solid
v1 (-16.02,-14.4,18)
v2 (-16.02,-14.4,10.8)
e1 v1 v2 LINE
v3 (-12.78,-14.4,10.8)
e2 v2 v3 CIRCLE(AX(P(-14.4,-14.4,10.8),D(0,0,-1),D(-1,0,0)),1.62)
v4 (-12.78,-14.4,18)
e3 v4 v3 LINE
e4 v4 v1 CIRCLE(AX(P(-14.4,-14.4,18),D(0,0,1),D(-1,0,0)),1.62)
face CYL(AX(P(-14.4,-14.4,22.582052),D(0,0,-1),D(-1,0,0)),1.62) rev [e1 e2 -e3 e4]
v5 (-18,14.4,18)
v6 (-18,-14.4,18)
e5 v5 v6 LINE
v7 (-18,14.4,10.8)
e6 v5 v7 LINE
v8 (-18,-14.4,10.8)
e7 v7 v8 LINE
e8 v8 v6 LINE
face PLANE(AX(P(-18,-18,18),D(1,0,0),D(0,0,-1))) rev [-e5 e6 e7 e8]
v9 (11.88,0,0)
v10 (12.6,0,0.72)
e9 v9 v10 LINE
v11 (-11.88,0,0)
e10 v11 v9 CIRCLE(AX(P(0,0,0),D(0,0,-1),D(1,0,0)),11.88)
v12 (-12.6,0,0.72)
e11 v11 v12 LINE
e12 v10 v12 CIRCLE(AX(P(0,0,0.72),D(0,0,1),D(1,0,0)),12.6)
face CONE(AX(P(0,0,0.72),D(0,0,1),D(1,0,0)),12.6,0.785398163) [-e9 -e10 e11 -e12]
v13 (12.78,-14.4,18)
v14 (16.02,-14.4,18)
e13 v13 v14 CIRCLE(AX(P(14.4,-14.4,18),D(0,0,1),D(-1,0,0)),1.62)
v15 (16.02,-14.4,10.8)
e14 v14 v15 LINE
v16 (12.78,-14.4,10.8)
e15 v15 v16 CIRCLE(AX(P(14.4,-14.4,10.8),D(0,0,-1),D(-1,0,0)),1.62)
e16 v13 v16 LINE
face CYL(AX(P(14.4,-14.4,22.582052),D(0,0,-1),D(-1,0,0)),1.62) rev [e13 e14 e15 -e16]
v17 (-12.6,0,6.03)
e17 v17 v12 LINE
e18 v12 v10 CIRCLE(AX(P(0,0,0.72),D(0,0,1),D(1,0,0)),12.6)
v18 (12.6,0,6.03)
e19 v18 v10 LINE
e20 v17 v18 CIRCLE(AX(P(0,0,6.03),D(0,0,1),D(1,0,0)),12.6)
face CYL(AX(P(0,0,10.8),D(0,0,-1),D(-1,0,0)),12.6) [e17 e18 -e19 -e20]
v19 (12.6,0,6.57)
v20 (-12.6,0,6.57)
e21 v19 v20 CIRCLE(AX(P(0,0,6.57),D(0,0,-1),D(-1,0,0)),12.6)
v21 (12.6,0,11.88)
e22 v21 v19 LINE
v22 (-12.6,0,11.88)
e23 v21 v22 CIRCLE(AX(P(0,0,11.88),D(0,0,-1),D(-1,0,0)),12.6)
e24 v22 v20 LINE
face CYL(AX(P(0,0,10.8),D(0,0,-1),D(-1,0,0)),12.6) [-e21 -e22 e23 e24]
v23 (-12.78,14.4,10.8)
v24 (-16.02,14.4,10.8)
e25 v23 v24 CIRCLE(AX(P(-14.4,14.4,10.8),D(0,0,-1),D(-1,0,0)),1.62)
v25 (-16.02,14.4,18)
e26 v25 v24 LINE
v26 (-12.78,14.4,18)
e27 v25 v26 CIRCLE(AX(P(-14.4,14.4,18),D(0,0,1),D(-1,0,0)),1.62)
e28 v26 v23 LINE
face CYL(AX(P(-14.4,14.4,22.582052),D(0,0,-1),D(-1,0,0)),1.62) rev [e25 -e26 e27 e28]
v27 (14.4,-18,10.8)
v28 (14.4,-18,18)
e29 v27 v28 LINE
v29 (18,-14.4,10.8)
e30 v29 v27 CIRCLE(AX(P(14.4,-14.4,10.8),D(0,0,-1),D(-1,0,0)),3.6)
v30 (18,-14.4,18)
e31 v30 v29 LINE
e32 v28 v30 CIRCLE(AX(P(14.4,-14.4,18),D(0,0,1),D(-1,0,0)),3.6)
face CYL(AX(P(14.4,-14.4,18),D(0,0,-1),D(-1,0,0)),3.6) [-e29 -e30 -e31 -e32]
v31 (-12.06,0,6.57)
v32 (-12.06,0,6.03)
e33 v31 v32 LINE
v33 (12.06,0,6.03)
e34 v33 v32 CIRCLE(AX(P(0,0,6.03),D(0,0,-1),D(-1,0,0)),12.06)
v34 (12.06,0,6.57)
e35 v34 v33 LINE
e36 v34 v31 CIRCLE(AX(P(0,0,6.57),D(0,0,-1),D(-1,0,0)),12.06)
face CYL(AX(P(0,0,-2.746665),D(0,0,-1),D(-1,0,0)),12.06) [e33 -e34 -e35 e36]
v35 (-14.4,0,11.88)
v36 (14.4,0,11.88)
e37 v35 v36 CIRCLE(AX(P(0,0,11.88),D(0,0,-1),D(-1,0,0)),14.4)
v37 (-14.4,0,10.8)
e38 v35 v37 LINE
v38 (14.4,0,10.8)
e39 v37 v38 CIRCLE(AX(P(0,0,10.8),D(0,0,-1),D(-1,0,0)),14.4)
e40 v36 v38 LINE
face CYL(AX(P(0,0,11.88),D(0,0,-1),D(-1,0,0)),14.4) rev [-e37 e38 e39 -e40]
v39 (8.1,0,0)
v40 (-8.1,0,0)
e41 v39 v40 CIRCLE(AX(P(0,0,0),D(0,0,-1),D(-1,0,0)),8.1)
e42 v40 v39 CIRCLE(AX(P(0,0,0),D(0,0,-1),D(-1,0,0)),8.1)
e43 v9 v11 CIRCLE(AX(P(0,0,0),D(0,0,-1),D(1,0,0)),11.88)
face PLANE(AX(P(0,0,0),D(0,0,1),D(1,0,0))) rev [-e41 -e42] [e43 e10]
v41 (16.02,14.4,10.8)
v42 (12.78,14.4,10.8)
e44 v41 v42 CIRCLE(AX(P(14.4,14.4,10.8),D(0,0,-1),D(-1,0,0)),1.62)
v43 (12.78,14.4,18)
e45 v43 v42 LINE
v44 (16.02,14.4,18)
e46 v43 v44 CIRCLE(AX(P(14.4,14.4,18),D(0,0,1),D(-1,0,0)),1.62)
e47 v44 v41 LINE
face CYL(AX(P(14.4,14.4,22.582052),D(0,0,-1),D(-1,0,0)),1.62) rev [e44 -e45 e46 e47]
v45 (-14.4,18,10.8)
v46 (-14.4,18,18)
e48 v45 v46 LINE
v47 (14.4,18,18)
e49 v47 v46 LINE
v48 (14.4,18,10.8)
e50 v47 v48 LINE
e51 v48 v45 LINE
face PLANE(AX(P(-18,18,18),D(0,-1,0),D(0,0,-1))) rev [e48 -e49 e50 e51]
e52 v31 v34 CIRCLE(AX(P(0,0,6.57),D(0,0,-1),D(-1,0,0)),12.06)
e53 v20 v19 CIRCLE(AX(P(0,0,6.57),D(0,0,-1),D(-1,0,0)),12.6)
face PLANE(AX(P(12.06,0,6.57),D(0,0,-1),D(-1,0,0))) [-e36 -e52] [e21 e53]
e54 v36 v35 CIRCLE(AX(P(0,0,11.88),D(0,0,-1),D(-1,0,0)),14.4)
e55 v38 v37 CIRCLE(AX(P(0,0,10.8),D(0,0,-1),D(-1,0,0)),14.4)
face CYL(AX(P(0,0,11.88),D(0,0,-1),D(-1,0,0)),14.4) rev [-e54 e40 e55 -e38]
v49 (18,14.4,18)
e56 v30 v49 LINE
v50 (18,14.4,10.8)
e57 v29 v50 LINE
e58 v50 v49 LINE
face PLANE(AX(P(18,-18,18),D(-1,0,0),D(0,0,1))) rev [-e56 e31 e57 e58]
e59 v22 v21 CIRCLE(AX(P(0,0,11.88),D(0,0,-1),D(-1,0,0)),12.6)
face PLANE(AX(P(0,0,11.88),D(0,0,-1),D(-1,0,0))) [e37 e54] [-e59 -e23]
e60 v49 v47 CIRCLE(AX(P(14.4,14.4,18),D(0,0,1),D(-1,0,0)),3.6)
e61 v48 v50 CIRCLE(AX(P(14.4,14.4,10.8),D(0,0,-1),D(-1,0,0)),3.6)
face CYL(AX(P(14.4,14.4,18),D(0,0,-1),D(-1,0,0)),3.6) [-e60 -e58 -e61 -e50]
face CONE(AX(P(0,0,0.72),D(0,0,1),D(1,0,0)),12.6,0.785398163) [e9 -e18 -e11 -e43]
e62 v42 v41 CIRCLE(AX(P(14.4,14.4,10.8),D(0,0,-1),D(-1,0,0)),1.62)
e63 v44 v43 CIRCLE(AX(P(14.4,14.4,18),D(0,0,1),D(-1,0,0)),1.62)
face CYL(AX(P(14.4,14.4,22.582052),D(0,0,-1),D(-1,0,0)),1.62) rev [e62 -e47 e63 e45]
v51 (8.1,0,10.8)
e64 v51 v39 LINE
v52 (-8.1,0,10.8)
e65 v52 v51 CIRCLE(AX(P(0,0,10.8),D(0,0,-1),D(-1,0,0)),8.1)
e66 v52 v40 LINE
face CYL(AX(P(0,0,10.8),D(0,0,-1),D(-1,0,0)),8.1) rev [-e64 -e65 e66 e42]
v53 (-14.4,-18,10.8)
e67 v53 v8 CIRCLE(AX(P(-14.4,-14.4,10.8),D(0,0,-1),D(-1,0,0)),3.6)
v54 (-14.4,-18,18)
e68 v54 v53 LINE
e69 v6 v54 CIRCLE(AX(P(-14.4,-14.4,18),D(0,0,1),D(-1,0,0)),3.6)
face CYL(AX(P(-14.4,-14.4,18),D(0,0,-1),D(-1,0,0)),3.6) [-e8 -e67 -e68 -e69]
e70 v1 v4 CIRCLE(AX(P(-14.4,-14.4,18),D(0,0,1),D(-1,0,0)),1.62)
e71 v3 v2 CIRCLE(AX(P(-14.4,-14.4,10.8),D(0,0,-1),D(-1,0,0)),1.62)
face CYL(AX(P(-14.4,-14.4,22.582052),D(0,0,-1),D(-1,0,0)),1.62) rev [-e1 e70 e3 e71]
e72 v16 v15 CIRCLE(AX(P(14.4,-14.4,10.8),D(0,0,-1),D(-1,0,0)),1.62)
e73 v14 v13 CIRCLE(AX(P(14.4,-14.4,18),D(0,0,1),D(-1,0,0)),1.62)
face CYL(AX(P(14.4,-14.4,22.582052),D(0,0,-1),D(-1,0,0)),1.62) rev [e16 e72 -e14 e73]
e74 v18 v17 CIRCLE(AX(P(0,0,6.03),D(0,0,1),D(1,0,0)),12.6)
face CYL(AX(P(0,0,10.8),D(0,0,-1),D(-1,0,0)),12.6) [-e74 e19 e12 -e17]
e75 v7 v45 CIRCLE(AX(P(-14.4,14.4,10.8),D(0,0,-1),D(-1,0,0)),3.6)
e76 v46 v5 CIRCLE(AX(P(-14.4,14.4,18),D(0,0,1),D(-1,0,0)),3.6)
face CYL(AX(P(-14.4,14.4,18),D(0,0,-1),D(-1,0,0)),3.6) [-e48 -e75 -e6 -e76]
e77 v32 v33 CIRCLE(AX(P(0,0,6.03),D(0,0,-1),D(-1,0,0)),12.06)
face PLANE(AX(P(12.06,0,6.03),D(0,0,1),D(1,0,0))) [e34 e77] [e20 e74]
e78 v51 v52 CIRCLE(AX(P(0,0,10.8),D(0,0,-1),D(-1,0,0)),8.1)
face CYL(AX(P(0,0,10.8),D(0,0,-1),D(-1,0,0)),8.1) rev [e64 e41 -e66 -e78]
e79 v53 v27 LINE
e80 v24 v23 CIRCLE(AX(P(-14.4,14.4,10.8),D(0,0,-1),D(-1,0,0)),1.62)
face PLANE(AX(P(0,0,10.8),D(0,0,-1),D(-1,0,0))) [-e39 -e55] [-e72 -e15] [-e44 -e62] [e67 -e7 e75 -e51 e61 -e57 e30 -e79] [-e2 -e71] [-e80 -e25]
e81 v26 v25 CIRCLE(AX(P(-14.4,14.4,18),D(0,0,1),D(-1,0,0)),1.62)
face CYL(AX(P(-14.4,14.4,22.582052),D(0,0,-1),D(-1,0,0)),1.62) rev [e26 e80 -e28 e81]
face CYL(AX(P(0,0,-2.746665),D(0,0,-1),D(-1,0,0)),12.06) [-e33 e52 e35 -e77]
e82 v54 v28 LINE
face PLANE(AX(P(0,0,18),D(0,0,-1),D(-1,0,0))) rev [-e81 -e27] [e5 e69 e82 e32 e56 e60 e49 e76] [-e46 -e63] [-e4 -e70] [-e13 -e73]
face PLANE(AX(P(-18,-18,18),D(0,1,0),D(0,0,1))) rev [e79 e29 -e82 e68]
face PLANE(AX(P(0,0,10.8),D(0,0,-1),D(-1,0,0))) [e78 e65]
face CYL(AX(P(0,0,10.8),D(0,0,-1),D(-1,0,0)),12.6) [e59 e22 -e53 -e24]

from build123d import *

# Parameters (mm, degrees)
SKETCH1_R           = 12.6
BOSS_EXTRUDE1_DEPTH = 10.8
SKETCH2_W           = 36
SKETCH2_H           = 36
BOSS_EXTRUDE2_DEPTH = 7.2
FILLET1_R           = 3.6
CHAMFER1_SIZE       = 0.72
SKETCH3_R           = 14.4
SKETCH3_R_2         = 12.6
CUT_EXTRUDE1_DEPTH  = 1.08
SKETCH4_W           = 1.08
SKETCH4_H           = 0.54
SKETCH5_R           = 1.62
CUT_EXTRUDE2_DEPTH  = 7.2
SKETCH6_R           = 8.1
CUT_EXTRUDE3_DEPTH  = 10.8


with BuildPart() as part:
    # Sketch1 → Boss-Extrude1 (new body)
    with BuildSketch(Plane.XY):
        with Locations(Location((0, 0, 0), (0, 0, 180))):
            Circle(SKETCH1_R)
    extrude(amount=BOSS_EXTRUDE1_DEPTH)

    # Sketch2 → Boss-Extrude2 (add)
    with BuildSketch(Plane.XY.offset(10.8)):
        Rectangle(SKETCH2_W, SKETCH2_H)
    extrude(amount=BOSS_EXTRUDE2_DEPTH)

    # Fillet1
    fillet1_edges = [part.edges().sort_by_distance(p)[0] for p in [
        (18, -18, 14.4),
        (18, 18, 14.4),
        (-18, 18, 14.4),
        (-18, -18, 14.4),
    ]]
    fillet(fillet1_edges, radius=FILLET1_R)

    # Chamfer1
    chamfer1_edges = [part.edges().sort_by_distance(p)[0] for p in [
        (12.6, 0, 0),
    ]]
    chamfer(chamfer1_edges, length=CHAMFER1_SIZE)

    # Sketch3 → Cut-Extrude1 (cut)
    with BuildSketch(Plane(origin=(0, 0, 10.8), x_dir=(-1, 0, 0), z_dir=(0, 0, -1))):
        Circle(SKETCH3_R)
        Circle(SKETCH3_R_2, mode=Mode.SUBTRACT)
    extrude(amount=-CUT_EXTRUDE1_DEPTH, mode=Mode.SUBTRACT)

    # Sketch4 → Cut-Revolve1 (revolve, cut)
    with BuildSketch(Plane(origin=(0, 0, 0), x_dir=(1, 0, 0), z_dir=(0, 1, 0)), mode=Mode.PRIVATE) as cut_revolve1_sk:
        with Locations((12.6, -6.3)):
            Rectangle(SKETCH4_W, SKETCH4_H)
    revolve(cut_revolve1_sk.sketch.rotate(Axis((0, 0, -2.746665179), (0, 0, 1)), 180), axis=Axis((0, 0, -2.746665179), (0, 0, 1)), mode=Mode.SUBTRACT)

    # Sketch5 → Cut-Extrude2 (cut)
    with BuildSketch(Plane(origin=(0, 0, 10.8), x_dir=(-1, 0, 0), z_dir=(0, 0, -1))):
        with Locations((14.4, 14.4)):
            Circle(SKETCH5_R)
        with Locations((14.4, -14.4)):
            Circle(SKETCH5_R)
        with Locations((-14.4, -14.4)):
            Circle(SKETCH5_R)
        with Locations((-14.4, 14.4)):
            Circle(SKETCH5_R)
    extrude(amount=-CUT_EXTRUDE2_DEPTH, mode=Mode.SUBTRACT)

    # Sketch6 → Cut-Extrude3 (cut)
    with BuildSketch(Plane(origin=(0, 0, 0), x_dir=(-1, 0, 0), z_dir=(0, 0, -1))):
        Circle(SKETCH6_R)
    extrude(amount=-CUT_EXTRUDE3_DEPTH, mode=Mode.SUBTRACT)


solid = part.part
